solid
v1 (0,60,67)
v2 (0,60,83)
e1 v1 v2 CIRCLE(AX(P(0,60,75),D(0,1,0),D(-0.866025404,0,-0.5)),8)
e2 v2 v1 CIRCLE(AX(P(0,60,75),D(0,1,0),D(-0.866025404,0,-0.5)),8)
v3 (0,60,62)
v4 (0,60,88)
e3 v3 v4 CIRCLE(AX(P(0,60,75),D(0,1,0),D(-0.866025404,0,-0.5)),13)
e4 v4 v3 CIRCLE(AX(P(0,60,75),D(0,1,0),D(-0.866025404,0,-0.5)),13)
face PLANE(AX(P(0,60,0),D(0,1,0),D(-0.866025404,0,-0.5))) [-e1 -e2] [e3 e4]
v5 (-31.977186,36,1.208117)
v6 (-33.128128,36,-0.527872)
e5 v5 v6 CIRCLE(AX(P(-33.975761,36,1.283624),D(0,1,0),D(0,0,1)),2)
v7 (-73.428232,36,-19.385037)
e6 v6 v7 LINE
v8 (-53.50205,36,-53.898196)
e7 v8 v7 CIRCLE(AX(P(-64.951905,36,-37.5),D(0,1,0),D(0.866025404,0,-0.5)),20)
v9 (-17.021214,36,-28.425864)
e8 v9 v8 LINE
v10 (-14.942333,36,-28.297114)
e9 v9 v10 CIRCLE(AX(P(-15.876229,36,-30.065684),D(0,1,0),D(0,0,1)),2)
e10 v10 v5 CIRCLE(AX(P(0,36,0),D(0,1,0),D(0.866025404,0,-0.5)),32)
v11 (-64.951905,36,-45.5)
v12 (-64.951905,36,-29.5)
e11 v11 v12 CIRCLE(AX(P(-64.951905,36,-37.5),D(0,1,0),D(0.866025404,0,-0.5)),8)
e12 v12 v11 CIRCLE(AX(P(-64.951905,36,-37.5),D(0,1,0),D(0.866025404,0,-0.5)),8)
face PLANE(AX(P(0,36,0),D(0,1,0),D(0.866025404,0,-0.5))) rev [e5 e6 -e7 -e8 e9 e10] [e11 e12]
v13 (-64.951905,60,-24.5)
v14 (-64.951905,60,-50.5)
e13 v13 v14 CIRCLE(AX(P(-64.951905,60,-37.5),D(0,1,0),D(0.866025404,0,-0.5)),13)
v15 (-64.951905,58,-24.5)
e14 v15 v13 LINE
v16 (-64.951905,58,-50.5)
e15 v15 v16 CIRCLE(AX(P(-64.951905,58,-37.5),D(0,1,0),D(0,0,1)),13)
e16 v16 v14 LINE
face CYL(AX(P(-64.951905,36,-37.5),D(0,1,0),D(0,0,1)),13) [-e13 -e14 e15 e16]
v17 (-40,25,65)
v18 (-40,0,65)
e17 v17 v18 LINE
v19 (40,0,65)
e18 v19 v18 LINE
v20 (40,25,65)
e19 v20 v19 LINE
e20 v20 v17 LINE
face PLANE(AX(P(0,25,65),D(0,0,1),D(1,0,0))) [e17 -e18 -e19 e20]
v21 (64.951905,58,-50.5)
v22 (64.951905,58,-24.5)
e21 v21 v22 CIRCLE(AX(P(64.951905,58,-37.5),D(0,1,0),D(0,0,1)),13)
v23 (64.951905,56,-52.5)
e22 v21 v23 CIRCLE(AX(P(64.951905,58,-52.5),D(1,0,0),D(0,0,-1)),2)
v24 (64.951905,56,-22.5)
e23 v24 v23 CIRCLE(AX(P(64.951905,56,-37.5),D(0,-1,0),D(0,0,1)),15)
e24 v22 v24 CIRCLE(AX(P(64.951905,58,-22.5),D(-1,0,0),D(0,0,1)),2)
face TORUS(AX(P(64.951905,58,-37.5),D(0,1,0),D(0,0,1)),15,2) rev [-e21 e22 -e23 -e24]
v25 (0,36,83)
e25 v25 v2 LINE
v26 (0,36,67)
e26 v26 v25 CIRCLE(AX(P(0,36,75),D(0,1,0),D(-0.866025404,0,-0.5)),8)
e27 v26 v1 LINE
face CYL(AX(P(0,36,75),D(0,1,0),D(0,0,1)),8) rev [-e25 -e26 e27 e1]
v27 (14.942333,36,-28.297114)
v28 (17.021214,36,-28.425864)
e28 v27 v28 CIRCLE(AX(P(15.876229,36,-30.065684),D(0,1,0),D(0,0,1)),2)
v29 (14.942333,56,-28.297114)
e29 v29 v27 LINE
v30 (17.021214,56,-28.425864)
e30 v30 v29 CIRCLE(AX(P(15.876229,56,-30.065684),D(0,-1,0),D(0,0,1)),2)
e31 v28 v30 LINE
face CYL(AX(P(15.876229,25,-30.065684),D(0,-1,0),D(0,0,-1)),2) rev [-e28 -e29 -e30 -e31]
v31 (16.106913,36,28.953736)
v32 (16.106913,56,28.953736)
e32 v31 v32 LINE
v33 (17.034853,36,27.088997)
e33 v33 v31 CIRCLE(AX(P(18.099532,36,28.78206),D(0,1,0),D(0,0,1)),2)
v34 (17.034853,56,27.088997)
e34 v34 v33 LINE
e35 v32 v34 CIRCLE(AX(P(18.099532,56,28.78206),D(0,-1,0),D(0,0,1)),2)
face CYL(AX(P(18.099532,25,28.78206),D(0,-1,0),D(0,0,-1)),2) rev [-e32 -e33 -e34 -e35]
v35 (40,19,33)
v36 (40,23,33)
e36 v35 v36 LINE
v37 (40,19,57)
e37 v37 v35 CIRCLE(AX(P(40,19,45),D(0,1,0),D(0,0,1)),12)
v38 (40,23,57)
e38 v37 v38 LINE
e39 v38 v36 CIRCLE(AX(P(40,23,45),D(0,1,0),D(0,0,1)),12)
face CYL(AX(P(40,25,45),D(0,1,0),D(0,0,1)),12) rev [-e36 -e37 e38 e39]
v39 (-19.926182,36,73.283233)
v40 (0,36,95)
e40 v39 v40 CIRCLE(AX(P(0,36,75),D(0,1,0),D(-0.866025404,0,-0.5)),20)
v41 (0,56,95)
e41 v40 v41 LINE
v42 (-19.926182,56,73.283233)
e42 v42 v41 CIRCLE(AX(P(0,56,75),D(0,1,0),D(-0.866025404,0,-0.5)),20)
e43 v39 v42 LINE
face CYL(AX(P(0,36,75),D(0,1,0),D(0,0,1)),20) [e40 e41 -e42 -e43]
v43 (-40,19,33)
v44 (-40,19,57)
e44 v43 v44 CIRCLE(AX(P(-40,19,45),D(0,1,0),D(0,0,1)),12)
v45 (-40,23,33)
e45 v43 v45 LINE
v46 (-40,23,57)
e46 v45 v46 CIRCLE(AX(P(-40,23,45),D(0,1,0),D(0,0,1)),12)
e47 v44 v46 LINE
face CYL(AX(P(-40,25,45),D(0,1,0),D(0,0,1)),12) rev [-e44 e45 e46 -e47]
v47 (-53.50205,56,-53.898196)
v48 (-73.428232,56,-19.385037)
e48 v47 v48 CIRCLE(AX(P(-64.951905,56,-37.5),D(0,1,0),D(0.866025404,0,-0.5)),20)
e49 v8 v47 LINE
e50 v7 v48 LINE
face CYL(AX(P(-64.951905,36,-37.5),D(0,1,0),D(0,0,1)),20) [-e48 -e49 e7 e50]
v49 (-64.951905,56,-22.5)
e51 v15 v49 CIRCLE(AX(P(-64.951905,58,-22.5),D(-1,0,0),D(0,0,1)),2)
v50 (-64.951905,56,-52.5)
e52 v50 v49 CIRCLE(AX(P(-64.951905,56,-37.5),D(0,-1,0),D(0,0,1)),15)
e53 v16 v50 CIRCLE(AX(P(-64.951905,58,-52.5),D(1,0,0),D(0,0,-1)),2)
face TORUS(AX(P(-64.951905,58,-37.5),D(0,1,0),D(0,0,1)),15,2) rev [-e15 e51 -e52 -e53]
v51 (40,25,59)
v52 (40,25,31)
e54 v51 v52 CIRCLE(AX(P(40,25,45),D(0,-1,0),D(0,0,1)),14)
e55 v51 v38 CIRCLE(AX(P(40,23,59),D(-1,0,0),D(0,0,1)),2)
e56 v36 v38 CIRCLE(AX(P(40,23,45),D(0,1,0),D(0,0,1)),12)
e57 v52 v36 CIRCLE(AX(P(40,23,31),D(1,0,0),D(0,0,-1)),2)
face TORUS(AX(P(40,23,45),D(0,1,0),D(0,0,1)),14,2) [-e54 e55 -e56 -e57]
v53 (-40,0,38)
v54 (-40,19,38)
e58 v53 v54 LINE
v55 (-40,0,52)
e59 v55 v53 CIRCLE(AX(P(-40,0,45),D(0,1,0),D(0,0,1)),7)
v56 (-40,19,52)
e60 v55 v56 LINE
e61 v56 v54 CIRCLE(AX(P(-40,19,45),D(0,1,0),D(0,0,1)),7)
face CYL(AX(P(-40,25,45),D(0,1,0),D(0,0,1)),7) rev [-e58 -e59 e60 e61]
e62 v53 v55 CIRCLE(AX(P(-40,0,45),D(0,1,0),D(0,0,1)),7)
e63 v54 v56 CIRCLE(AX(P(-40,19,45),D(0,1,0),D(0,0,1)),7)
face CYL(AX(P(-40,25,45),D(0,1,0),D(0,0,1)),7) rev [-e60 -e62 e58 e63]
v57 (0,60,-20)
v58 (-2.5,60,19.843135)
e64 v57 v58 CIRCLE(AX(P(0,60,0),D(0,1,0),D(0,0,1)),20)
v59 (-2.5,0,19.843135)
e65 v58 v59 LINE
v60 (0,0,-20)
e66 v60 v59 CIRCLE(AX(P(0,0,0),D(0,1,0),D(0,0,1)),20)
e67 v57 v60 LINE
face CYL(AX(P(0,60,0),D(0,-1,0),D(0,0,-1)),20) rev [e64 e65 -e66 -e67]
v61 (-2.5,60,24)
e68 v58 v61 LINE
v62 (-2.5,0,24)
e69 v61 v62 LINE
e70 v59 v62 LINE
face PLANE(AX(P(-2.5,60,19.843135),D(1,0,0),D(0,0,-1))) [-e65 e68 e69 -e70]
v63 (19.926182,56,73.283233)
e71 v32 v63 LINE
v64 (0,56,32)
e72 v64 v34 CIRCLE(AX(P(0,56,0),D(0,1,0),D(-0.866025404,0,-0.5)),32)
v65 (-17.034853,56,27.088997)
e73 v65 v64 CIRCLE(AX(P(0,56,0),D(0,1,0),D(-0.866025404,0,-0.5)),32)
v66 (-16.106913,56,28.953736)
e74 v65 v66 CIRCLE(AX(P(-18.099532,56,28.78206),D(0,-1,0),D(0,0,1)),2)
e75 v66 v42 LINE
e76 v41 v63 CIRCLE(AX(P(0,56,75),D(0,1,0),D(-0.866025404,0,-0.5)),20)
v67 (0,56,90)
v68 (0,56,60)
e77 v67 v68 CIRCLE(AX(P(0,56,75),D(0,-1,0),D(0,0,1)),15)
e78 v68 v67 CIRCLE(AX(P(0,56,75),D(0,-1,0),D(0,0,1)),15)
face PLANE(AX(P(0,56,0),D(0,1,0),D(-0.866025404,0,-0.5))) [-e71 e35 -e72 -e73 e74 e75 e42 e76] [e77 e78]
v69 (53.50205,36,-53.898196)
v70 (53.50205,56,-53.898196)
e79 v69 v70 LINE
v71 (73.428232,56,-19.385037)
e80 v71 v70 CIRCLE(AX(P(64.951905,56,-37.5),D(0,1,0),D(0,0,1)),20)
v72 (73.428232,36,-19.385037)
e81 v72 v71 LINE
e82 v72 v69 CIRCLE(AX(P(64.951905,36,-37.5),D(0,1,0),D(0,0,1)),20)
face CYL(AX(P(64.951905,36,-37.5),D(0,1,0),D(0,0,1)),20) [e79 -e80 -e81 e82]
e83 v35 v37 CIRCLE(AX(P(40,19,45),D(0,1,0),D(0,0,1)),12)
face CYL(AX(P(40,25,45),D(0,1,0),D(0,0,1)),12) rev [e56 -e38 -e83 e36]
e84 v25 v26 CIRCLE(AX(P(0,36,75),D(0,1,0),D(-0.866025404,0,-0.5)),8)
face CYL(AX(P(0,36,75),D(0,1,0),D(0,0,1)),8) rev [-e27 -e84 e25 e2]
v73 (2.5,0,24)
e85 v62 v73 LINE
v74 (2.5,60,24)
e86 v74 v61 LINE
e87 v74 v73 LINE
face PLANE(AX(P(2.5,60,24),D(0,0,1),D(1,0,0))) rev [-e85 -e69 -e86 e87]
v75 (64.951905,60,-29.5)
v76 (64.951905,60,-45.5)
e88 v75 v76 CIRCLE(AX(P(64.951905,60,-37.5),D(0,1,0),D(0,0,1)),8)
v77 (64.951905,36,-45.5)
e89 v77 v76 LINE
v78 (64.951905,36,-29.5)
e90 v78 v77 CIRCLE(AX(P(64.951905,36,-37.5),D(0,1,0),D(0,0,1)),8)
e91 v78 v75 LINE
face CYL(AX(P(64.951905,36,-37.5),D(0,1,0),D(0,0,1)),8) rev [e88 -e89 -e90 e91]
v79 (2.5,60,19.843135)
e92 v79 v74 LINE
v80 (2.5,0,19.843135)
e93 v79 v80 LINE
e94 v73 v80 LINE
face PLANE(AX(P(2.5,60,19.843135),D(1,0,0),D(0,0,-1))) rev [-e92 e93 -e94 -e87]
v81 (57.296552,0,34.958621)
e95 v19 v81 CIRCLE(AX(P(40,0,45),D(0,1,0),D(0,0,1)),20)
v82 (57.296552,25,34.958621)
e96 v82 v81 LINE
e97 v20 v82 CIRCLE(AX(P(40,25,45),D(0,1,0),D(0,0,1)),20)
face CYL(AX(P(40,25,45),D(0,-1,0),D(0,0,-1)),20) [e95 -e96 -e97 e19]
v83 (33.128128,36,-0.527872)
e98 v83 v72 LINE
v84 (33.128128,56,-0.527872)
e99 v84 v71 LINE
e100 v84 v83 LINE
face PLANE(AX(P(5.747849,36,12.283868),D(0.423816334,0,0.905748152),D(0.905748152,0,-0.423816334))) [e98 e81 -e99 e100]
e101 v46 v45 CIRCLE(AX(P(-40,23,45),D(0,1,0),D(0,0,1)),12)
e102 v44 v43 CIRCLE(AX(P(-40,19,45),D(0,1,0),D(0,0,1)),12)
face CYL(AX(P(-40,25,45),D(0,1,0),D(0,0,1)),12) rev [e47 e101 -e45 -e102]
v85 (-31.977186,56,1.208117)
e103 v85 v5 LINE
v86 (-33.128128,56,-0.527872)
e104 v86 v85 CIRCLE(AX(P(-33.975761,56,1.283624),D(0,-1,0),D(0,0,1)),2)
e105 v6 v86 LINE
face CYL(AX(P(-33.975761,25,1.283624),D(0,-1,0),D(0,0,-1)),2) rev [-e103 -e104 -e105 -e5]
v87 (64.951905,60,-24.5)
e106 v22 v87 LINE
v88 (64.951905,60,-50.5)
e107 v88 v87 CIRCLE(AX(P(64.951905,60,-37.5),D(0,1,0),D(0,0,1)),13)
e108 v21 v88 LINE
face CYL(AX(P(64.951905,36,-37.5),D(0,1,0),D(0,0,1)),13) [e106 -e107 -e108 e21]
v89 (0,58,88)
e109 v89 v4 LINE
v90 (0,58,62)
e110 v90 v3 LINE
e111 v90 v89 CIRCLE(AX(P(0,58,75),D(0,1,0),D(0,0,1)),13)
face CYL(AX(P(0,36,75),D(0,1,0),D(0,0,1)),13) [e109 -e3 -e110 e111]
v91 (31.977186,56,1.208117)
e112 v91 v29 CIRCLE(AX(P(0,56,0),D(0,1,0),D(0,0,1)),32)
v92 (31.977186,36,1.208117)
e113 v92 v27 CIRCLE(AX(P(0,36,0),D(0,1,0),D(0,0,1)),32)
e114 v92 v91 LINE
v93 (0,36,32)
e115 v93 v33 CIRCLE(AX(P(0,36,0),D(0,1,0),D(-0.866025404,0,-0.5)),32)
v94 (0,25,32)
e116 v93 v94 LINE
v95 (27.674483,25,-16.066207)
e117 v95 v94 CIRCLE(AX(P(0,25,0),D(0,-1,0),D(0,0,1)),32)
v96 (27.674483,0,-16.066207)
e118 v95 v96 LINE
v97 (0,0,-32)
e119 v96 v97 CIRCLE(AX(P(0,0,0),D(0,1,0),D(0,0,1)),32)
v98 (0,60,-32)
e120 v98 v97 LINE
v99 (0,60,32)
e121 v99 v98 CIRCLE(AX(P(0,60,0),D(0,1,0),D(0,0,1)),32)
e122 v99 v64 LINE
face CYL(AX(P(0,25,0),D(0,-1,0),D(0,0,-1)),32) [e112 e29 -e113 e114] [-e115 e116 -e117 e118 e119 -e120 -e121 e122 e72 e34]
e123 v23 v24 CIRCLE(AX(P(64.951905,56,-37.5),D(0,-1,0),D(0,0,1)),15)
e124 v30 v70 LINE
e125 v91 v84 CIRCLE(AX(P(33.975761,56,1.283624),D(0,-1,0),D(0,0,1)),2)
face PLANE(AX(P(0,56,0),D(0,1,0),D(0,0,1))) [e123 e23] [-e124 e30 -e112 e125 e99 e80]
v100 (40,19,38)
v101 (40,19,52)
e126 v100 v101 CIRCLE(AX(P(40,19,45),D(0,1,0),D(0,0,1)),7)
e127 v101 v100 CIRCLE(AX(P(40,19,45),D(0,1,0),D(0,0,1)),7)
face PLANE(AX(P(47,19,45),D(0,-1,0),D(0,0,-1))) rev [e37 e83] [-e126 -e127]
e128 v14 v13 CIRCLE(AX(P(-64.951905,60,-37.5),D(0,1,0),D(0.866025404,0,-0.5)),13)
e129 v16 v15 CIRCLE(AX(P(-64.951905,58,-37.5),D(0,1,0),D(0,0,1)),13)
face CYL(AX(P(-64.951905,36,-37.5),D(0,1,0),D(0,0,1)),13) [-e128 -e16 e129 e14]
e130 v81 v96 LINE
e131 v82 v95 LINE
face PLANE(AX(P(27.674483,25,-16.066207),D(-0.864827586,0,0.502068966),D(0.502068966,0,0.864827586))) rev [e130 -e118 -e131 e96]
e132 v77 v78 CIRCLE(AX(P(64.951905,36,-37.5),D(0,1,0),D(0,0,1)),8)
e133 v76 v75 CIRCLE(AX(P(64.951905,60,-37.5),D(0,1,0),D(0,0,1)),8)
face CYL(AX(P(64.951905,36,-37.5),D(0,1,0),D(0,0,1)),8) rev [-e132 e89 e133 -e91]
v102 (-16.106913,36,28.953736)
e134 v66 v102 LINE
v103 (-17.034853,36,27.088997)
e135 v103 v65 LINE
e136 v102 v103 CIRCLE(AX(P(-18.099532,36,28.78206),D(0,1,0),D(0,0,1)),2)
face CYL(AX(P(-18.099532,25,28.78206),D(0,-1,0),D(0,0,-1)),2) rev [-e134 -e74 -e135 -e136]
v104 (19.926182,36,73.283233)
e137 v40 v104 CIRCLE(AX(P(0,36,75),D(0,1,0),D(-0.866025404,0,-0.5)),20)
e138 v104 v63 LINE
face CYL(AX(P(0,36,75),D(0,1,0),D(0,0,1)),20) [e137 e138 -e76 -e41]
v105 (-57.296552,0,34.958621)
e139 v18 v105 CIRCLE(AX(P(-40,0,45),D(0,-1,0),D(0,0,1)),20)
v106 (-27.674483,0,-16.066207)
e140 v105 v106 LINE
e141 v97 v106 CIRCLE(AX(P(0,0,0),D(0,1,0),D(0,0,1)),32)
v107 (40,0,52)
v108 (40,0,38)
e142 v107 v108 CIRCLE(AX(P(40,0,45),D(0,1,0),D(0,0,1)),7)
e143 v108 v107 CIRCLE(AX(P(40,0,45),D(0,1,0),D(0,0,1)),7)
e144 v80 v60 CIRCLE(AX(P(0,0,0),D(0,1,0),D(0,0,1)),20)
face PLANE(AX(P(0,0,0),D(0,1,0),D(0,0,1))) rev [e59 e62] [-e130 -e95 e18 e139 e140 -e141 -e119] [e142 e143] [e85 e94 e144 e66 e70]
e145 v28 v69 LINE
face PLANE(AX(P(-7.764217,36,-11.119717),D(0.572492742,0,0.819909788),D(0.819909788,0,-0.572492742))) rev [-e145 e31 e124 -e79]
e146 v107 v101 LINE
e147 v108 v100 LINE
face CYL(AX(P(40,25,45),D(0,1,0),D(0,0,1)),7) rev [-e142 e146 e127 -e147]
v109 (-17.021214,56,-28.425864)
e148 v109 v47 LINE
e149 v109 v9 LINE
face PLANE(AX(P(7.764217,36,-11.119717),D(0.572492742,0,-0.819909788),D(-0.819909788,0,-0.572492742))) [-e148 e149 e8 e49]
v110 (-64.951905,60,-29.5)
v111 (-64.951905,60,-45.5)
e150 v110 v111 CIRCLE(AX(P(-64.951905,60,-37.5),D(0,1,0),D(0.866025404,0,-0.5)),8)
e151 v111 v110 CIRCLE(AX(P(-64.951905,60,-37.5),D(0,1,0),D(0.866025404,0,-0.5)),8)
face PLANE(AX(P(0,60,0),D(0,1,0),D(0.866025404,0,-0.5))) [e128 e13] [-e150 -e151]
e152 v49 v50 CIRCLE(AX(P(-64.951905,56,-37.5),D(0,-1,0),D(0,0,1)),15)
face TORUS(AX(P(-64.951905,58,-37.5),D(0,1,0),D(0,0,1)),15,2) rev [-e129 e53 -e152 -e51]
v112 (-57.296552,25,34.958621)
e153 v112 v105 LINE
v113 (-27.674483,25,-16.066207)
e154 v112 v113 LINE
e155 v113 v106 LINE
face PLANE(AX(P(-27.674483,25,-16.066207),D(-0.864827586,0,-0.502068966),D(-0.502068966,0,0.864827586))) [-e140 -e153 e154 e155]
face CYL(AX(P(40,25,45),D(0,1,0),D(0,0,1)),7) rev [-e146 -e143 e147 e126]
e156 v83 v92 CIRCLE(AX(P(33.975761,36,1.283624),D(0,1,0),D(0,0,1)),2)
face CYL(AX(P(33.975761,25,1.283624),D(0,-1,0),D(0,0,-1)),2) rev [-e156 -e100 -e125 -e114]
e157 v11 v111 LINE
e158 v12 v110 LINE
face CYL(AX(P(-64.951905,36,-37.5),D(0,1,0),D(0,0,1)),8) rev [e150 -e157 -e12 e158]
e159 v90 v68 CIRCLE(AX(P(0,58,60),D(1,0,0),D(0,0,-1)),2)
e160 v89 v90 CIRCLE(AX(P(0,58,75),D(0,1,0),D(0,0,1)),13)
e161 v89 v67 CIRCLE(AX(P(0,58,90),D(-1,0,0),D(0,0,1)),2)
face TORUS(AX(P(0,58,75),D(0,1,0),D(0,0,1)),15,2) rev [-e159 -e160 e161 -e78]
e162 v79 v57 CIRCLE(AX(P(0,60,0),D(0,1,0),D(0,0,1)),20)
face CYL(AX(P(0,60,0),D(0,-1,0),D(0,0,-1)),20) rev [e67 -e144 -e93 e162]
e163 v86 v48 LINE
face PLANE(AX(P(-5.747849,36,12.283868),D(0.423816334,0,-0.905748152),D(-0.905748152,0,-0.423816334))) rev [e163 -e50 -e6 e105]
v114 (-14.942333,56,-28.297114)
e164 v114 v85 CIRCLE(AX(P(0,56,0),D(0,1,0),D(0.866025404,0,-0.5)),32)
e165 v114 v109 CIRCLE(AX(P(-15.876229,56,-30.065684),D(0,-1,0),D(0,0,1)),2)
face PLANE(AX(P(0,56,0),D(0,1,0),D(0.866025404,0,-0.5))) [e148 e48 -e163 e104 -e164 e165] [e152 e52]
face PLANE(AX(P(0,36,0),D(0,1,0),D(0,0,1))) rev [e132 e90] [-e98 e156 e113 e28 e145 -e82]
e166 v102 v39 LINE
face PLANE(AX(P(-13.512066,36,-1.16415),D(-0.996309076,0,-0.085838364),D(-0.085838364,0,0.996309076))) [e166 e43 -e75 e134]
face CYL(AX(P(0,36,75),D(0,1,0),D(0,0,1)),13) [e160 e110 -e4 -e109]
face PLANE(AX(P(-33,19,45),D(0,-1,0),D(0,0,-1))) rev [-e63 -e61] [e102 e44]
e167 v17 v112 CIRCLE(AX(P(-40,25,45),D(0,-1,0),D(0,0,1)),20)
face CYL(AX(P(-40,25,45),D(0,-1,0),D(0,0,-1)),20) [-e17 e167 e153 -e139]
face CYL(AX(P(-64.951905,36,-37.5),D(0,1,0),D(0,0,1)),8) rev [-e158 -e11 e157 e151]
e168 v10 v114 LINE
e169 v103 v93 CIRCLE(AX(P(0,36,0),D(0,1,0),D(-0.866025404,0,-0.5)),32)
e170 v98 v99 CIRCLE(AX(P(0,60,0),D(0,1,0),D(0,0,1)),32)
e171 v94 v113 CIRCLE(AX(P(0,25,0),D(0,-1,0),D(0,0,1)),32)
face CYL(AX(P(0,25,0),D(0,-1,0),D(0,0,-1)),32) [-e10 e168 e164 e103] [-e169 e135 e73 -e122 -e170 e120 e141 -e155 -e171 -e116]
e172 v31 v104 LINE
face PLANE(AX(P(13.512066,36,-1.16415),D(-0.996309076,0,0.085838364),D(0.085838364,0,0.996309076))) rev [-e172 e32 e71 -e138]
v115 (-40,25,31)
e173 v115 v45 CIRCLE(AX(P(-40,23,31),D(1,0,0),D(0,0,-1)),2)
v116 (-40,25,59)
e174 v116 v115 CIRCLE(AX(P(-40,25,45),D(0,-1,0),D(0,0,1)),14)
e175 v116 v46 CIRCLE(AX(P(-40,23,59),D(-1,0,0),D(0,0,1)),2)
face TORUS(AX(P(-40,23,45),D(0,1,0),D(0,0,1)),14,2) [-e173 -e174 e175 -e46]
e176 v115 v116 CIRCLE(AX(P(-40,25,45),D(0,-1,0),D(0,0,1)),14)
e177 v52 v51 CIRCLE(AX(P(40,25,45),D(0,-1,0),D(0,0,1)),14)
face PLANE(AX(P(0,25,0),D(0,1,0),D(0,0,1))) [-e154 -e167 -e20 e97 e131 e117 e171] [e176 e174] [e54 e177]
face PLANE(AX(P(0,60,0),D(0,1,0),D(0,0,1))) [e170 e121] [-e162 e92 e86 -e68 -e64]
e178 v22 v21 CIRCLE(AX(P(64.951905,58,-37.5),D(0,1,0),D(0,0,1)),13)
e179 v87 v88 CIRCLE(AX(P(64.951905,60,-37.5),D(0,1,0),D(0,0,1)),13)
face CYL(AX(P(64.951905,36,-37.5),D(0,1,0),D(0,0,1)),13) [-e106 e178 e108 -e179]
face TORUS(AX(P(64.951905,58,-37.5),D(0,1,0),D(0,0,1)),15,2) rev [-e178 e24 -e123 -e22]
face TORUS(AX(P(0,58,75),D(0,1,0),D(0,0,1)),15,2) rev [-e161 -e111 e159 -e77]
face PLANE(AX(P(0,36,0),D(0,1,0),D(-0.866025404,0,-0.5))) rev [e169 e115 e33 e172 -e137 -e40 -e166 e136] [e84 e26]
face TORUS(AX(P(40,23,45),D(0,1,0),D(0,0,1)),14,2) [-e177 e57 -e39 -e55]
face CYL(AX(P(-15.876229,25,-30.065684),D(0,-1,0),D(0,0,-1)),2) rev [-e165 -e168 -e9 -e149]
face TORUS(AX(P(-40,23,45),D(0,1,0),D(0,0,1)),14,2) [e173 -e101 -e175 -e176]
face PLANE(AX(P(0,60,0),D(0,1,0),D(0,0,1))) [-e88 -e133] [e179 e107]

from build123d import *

# Parameters (mm, degrees)
BASE_PLATE_DEPTH                  = 25
SKETCH1_15_R                      = 32
HUB_DEPTH                         = 60
KEYWAY_CUT_DEPTH                  = 96.131487952
COUNTERBORED_HOLES_M8_D           = 14
COUNTERBORED_HOLES_M8_CBORE_D     = 24
COUNTERBORED_HOLES_M8_CBORE_DEPTH = 6
ARM_START                         = -24
ARM_SKETCH_R                      = 8
ARM_DEPTH                         = 20
SKETCH7_3_R                       = 13
SKETCH7_3_R_2                     = 8
ARM_END_BOSS_DEPTH                = 24
ARM_PATTERN_3X_COUNT              = 3
ARM_FILLETS_R2_R                  = 2
COUNTERBORE_EDGE_FILLETS_R2_R     = 2


with BuildPart() as part:
    # Base and Hub Sketch → Base Plate (new body)
    with BuildSketch(Plane(origin=(0, 0, 0), x_dir=(1, 0, 0), z_dir=(0, 1, 0))):
        with BuildLine():
            Line((-40, -65), (40, -65))
            ThreePointArc((40, -65), (57.332449137, -54.979288897), (57.296551724, -34.95862069))
            Line((57.296551724, -34.95862069), (27.674482759, 16.066206897))
            ThreePointArc((27.674482759, 16.066206897), (0, 32), (-27.674482759, 16.066206897))
            Line((-27.674482759, 16.066206897), (-57.296551724, -34.95862069))
            ThreePointArc((-57.296551724, -34.95862069), (-57.332449137, -54.979288897), (-40, -65))
        make_face()
    extrude(amount=BASE_PLATE_DEPTH)

    # Sketch1_15 → Hub (add)
    with BuildSketch(Plane(origin=(0, 0, 0), x_dir=(1, 0, 0), z_dir=(0, 1, 0))):
        with Locations(Location((0, 0, 0), (0, 0, 149.863023681))):
            Circle(SKETCH1_15_R)
        with BuildLine():
            Line((2.5, -19.843134833), (2.5, -24))
            Line((2.5, -24), (-2.5, -24))
            Line((-2.5, -24), (-2.5, -19.843134833))
            ThreePointArc((-2.5, -19.843134833), (0, 20), (2.5, -19.843134833))
        make_face(mode=Mode.SUBTRACT)
    extrude(amount=HUB_DEPTH)

    # Keyway Sketch → Keyway Cut (cut, through all)
    with BuildSketch(Plane(origin=(0, 25, 0), x_dir=(1, 0, 0), z_dir=(0, 1, 0))):
        with BuildLine():
            Line((-2.5, -24), (2.5, -24))
            Line((2.5, -24), (2.5, -19.843134833))
            ThreePointArc((2.5, -19.843134833), (0, 20), (-2.5, -19.843134833))
            Line((-2.5, -19.843134833), (-2.5, -24))
        make_face()
    extrude(amount=-KEYWAY_CUT_DEPTH, mode=Mode.SUBTRACT)

    # Counterbored Holes M8 (through all)
    with Locations(Plane(origin=(0, 25, 0), x_dir=(1, 0, 0), z_dir=(0, 1, 0))):
        with Locations((-40, -45), (40, -45)):
            CounterBoreHole(COUNTERBORED_HOLES_M8_D / 2, COUNTERBORED_HOLES_M8_CBORE_D / 2, COUNTERBORED_HOLES_M8_CBORE_DEPTH)

    # Arm Sketch → Arm (add)
    with BuildSketch(Plane(origin=(0, 60, 0), x_dir=(1, 0, 0), z_dir=(0, 1, 0)).offset(ARM_START)):
        with BuildLine():
            Line((53.502050444, 53.898195759), (16, 27.712812921))
            ThreePointArc((16, 27.712812921), (27.712812921, 16), (32, 0))
            Line((32, 0), (73.428231967, 19.385036959))
            ThreePointArc((73.428231967, 19.385036959), (82.27241336, 47.5), (53.502050444, 53.898195759))
        make_face()
        with Locations(Location((64.951905284, 37.5, 0), (0, 0, 270))):
            Circle(ARM_SKETCH_R, mode=Mode.SUBTRACT)
    arm = extrude(amount=ARM_DEPTH)

    # Sketch7_3 → Arm End Boss (add)
    with BuildSketch(Plane(origin=(0, 60, 0), x_dir=(1, 0, 0), z_dir=(0, 1, 0)).offset(ARM_START)):
        with Locations(Location((64.951905284, 37.5, 0), (0, 0, 270))):
            Circle(SKETCH7_3_R)
        with Locations(Location((64.951905284, 37.5, 0), (0, 0, 270))):
            Circle(SKETCH7_3_R_2, mode=Mode.SUBTRACT)
    arm_end_boss = extrude(amount=ARM_END_BOSS_DEPTH)

    # Arm Pattern 3x: Arm, Arm End Boss ×3 about axis
    arm_pattern_3x_axis = Axis((0, 0, 0), (0, 1, 0))
    add([arm.rotate(arm_pattern_3x_axis, i * 360 / ARM_PATTERN_3X_COUNT) for i in range(1, ARM_PATTERN_3X_COUNT)])
    add([arm_end_boss.rotate(arm_pattern_3x_axis, i * 360 / ARM_PATTERN_3X_COUNT) for i in range(1, ARM_PATTERN_3X_COUNT)])

    # Arm Fillets R2
    arm_fillets_r2_edges = [part.edges().sort_by_distance(p)[0] for p in [
        (64.951905284, 56, -50.5),
        (-16, 46, 27.712812921),
        (16, 46, 27.712812921),
        (-16, 46, -27.712812921),
        (-32, 46, 0),
        (11.258330249, 56, 81.5),
        (-76.210235533, 56, -31),
        (32, 46, 0),
        (16, 46, -27.712812921),
    ]]
    fillet(arm_fillets_r2_edges, radius=ARM_FILLETS_R2_R)

    # Counterbore Edge Fillets R2
    counterbore_edge_fillets_r2_edges = [part.edges().sort_by_distance(p)[0] for p in [
        (28, 25, 45),
        (-52, 25, 45),
    ]]
    fillet(counterbore_edge_fillets_r2_edges, radius=COUNTERBORE_EDGE_FILLETS_R2_R)


solid = part.part
